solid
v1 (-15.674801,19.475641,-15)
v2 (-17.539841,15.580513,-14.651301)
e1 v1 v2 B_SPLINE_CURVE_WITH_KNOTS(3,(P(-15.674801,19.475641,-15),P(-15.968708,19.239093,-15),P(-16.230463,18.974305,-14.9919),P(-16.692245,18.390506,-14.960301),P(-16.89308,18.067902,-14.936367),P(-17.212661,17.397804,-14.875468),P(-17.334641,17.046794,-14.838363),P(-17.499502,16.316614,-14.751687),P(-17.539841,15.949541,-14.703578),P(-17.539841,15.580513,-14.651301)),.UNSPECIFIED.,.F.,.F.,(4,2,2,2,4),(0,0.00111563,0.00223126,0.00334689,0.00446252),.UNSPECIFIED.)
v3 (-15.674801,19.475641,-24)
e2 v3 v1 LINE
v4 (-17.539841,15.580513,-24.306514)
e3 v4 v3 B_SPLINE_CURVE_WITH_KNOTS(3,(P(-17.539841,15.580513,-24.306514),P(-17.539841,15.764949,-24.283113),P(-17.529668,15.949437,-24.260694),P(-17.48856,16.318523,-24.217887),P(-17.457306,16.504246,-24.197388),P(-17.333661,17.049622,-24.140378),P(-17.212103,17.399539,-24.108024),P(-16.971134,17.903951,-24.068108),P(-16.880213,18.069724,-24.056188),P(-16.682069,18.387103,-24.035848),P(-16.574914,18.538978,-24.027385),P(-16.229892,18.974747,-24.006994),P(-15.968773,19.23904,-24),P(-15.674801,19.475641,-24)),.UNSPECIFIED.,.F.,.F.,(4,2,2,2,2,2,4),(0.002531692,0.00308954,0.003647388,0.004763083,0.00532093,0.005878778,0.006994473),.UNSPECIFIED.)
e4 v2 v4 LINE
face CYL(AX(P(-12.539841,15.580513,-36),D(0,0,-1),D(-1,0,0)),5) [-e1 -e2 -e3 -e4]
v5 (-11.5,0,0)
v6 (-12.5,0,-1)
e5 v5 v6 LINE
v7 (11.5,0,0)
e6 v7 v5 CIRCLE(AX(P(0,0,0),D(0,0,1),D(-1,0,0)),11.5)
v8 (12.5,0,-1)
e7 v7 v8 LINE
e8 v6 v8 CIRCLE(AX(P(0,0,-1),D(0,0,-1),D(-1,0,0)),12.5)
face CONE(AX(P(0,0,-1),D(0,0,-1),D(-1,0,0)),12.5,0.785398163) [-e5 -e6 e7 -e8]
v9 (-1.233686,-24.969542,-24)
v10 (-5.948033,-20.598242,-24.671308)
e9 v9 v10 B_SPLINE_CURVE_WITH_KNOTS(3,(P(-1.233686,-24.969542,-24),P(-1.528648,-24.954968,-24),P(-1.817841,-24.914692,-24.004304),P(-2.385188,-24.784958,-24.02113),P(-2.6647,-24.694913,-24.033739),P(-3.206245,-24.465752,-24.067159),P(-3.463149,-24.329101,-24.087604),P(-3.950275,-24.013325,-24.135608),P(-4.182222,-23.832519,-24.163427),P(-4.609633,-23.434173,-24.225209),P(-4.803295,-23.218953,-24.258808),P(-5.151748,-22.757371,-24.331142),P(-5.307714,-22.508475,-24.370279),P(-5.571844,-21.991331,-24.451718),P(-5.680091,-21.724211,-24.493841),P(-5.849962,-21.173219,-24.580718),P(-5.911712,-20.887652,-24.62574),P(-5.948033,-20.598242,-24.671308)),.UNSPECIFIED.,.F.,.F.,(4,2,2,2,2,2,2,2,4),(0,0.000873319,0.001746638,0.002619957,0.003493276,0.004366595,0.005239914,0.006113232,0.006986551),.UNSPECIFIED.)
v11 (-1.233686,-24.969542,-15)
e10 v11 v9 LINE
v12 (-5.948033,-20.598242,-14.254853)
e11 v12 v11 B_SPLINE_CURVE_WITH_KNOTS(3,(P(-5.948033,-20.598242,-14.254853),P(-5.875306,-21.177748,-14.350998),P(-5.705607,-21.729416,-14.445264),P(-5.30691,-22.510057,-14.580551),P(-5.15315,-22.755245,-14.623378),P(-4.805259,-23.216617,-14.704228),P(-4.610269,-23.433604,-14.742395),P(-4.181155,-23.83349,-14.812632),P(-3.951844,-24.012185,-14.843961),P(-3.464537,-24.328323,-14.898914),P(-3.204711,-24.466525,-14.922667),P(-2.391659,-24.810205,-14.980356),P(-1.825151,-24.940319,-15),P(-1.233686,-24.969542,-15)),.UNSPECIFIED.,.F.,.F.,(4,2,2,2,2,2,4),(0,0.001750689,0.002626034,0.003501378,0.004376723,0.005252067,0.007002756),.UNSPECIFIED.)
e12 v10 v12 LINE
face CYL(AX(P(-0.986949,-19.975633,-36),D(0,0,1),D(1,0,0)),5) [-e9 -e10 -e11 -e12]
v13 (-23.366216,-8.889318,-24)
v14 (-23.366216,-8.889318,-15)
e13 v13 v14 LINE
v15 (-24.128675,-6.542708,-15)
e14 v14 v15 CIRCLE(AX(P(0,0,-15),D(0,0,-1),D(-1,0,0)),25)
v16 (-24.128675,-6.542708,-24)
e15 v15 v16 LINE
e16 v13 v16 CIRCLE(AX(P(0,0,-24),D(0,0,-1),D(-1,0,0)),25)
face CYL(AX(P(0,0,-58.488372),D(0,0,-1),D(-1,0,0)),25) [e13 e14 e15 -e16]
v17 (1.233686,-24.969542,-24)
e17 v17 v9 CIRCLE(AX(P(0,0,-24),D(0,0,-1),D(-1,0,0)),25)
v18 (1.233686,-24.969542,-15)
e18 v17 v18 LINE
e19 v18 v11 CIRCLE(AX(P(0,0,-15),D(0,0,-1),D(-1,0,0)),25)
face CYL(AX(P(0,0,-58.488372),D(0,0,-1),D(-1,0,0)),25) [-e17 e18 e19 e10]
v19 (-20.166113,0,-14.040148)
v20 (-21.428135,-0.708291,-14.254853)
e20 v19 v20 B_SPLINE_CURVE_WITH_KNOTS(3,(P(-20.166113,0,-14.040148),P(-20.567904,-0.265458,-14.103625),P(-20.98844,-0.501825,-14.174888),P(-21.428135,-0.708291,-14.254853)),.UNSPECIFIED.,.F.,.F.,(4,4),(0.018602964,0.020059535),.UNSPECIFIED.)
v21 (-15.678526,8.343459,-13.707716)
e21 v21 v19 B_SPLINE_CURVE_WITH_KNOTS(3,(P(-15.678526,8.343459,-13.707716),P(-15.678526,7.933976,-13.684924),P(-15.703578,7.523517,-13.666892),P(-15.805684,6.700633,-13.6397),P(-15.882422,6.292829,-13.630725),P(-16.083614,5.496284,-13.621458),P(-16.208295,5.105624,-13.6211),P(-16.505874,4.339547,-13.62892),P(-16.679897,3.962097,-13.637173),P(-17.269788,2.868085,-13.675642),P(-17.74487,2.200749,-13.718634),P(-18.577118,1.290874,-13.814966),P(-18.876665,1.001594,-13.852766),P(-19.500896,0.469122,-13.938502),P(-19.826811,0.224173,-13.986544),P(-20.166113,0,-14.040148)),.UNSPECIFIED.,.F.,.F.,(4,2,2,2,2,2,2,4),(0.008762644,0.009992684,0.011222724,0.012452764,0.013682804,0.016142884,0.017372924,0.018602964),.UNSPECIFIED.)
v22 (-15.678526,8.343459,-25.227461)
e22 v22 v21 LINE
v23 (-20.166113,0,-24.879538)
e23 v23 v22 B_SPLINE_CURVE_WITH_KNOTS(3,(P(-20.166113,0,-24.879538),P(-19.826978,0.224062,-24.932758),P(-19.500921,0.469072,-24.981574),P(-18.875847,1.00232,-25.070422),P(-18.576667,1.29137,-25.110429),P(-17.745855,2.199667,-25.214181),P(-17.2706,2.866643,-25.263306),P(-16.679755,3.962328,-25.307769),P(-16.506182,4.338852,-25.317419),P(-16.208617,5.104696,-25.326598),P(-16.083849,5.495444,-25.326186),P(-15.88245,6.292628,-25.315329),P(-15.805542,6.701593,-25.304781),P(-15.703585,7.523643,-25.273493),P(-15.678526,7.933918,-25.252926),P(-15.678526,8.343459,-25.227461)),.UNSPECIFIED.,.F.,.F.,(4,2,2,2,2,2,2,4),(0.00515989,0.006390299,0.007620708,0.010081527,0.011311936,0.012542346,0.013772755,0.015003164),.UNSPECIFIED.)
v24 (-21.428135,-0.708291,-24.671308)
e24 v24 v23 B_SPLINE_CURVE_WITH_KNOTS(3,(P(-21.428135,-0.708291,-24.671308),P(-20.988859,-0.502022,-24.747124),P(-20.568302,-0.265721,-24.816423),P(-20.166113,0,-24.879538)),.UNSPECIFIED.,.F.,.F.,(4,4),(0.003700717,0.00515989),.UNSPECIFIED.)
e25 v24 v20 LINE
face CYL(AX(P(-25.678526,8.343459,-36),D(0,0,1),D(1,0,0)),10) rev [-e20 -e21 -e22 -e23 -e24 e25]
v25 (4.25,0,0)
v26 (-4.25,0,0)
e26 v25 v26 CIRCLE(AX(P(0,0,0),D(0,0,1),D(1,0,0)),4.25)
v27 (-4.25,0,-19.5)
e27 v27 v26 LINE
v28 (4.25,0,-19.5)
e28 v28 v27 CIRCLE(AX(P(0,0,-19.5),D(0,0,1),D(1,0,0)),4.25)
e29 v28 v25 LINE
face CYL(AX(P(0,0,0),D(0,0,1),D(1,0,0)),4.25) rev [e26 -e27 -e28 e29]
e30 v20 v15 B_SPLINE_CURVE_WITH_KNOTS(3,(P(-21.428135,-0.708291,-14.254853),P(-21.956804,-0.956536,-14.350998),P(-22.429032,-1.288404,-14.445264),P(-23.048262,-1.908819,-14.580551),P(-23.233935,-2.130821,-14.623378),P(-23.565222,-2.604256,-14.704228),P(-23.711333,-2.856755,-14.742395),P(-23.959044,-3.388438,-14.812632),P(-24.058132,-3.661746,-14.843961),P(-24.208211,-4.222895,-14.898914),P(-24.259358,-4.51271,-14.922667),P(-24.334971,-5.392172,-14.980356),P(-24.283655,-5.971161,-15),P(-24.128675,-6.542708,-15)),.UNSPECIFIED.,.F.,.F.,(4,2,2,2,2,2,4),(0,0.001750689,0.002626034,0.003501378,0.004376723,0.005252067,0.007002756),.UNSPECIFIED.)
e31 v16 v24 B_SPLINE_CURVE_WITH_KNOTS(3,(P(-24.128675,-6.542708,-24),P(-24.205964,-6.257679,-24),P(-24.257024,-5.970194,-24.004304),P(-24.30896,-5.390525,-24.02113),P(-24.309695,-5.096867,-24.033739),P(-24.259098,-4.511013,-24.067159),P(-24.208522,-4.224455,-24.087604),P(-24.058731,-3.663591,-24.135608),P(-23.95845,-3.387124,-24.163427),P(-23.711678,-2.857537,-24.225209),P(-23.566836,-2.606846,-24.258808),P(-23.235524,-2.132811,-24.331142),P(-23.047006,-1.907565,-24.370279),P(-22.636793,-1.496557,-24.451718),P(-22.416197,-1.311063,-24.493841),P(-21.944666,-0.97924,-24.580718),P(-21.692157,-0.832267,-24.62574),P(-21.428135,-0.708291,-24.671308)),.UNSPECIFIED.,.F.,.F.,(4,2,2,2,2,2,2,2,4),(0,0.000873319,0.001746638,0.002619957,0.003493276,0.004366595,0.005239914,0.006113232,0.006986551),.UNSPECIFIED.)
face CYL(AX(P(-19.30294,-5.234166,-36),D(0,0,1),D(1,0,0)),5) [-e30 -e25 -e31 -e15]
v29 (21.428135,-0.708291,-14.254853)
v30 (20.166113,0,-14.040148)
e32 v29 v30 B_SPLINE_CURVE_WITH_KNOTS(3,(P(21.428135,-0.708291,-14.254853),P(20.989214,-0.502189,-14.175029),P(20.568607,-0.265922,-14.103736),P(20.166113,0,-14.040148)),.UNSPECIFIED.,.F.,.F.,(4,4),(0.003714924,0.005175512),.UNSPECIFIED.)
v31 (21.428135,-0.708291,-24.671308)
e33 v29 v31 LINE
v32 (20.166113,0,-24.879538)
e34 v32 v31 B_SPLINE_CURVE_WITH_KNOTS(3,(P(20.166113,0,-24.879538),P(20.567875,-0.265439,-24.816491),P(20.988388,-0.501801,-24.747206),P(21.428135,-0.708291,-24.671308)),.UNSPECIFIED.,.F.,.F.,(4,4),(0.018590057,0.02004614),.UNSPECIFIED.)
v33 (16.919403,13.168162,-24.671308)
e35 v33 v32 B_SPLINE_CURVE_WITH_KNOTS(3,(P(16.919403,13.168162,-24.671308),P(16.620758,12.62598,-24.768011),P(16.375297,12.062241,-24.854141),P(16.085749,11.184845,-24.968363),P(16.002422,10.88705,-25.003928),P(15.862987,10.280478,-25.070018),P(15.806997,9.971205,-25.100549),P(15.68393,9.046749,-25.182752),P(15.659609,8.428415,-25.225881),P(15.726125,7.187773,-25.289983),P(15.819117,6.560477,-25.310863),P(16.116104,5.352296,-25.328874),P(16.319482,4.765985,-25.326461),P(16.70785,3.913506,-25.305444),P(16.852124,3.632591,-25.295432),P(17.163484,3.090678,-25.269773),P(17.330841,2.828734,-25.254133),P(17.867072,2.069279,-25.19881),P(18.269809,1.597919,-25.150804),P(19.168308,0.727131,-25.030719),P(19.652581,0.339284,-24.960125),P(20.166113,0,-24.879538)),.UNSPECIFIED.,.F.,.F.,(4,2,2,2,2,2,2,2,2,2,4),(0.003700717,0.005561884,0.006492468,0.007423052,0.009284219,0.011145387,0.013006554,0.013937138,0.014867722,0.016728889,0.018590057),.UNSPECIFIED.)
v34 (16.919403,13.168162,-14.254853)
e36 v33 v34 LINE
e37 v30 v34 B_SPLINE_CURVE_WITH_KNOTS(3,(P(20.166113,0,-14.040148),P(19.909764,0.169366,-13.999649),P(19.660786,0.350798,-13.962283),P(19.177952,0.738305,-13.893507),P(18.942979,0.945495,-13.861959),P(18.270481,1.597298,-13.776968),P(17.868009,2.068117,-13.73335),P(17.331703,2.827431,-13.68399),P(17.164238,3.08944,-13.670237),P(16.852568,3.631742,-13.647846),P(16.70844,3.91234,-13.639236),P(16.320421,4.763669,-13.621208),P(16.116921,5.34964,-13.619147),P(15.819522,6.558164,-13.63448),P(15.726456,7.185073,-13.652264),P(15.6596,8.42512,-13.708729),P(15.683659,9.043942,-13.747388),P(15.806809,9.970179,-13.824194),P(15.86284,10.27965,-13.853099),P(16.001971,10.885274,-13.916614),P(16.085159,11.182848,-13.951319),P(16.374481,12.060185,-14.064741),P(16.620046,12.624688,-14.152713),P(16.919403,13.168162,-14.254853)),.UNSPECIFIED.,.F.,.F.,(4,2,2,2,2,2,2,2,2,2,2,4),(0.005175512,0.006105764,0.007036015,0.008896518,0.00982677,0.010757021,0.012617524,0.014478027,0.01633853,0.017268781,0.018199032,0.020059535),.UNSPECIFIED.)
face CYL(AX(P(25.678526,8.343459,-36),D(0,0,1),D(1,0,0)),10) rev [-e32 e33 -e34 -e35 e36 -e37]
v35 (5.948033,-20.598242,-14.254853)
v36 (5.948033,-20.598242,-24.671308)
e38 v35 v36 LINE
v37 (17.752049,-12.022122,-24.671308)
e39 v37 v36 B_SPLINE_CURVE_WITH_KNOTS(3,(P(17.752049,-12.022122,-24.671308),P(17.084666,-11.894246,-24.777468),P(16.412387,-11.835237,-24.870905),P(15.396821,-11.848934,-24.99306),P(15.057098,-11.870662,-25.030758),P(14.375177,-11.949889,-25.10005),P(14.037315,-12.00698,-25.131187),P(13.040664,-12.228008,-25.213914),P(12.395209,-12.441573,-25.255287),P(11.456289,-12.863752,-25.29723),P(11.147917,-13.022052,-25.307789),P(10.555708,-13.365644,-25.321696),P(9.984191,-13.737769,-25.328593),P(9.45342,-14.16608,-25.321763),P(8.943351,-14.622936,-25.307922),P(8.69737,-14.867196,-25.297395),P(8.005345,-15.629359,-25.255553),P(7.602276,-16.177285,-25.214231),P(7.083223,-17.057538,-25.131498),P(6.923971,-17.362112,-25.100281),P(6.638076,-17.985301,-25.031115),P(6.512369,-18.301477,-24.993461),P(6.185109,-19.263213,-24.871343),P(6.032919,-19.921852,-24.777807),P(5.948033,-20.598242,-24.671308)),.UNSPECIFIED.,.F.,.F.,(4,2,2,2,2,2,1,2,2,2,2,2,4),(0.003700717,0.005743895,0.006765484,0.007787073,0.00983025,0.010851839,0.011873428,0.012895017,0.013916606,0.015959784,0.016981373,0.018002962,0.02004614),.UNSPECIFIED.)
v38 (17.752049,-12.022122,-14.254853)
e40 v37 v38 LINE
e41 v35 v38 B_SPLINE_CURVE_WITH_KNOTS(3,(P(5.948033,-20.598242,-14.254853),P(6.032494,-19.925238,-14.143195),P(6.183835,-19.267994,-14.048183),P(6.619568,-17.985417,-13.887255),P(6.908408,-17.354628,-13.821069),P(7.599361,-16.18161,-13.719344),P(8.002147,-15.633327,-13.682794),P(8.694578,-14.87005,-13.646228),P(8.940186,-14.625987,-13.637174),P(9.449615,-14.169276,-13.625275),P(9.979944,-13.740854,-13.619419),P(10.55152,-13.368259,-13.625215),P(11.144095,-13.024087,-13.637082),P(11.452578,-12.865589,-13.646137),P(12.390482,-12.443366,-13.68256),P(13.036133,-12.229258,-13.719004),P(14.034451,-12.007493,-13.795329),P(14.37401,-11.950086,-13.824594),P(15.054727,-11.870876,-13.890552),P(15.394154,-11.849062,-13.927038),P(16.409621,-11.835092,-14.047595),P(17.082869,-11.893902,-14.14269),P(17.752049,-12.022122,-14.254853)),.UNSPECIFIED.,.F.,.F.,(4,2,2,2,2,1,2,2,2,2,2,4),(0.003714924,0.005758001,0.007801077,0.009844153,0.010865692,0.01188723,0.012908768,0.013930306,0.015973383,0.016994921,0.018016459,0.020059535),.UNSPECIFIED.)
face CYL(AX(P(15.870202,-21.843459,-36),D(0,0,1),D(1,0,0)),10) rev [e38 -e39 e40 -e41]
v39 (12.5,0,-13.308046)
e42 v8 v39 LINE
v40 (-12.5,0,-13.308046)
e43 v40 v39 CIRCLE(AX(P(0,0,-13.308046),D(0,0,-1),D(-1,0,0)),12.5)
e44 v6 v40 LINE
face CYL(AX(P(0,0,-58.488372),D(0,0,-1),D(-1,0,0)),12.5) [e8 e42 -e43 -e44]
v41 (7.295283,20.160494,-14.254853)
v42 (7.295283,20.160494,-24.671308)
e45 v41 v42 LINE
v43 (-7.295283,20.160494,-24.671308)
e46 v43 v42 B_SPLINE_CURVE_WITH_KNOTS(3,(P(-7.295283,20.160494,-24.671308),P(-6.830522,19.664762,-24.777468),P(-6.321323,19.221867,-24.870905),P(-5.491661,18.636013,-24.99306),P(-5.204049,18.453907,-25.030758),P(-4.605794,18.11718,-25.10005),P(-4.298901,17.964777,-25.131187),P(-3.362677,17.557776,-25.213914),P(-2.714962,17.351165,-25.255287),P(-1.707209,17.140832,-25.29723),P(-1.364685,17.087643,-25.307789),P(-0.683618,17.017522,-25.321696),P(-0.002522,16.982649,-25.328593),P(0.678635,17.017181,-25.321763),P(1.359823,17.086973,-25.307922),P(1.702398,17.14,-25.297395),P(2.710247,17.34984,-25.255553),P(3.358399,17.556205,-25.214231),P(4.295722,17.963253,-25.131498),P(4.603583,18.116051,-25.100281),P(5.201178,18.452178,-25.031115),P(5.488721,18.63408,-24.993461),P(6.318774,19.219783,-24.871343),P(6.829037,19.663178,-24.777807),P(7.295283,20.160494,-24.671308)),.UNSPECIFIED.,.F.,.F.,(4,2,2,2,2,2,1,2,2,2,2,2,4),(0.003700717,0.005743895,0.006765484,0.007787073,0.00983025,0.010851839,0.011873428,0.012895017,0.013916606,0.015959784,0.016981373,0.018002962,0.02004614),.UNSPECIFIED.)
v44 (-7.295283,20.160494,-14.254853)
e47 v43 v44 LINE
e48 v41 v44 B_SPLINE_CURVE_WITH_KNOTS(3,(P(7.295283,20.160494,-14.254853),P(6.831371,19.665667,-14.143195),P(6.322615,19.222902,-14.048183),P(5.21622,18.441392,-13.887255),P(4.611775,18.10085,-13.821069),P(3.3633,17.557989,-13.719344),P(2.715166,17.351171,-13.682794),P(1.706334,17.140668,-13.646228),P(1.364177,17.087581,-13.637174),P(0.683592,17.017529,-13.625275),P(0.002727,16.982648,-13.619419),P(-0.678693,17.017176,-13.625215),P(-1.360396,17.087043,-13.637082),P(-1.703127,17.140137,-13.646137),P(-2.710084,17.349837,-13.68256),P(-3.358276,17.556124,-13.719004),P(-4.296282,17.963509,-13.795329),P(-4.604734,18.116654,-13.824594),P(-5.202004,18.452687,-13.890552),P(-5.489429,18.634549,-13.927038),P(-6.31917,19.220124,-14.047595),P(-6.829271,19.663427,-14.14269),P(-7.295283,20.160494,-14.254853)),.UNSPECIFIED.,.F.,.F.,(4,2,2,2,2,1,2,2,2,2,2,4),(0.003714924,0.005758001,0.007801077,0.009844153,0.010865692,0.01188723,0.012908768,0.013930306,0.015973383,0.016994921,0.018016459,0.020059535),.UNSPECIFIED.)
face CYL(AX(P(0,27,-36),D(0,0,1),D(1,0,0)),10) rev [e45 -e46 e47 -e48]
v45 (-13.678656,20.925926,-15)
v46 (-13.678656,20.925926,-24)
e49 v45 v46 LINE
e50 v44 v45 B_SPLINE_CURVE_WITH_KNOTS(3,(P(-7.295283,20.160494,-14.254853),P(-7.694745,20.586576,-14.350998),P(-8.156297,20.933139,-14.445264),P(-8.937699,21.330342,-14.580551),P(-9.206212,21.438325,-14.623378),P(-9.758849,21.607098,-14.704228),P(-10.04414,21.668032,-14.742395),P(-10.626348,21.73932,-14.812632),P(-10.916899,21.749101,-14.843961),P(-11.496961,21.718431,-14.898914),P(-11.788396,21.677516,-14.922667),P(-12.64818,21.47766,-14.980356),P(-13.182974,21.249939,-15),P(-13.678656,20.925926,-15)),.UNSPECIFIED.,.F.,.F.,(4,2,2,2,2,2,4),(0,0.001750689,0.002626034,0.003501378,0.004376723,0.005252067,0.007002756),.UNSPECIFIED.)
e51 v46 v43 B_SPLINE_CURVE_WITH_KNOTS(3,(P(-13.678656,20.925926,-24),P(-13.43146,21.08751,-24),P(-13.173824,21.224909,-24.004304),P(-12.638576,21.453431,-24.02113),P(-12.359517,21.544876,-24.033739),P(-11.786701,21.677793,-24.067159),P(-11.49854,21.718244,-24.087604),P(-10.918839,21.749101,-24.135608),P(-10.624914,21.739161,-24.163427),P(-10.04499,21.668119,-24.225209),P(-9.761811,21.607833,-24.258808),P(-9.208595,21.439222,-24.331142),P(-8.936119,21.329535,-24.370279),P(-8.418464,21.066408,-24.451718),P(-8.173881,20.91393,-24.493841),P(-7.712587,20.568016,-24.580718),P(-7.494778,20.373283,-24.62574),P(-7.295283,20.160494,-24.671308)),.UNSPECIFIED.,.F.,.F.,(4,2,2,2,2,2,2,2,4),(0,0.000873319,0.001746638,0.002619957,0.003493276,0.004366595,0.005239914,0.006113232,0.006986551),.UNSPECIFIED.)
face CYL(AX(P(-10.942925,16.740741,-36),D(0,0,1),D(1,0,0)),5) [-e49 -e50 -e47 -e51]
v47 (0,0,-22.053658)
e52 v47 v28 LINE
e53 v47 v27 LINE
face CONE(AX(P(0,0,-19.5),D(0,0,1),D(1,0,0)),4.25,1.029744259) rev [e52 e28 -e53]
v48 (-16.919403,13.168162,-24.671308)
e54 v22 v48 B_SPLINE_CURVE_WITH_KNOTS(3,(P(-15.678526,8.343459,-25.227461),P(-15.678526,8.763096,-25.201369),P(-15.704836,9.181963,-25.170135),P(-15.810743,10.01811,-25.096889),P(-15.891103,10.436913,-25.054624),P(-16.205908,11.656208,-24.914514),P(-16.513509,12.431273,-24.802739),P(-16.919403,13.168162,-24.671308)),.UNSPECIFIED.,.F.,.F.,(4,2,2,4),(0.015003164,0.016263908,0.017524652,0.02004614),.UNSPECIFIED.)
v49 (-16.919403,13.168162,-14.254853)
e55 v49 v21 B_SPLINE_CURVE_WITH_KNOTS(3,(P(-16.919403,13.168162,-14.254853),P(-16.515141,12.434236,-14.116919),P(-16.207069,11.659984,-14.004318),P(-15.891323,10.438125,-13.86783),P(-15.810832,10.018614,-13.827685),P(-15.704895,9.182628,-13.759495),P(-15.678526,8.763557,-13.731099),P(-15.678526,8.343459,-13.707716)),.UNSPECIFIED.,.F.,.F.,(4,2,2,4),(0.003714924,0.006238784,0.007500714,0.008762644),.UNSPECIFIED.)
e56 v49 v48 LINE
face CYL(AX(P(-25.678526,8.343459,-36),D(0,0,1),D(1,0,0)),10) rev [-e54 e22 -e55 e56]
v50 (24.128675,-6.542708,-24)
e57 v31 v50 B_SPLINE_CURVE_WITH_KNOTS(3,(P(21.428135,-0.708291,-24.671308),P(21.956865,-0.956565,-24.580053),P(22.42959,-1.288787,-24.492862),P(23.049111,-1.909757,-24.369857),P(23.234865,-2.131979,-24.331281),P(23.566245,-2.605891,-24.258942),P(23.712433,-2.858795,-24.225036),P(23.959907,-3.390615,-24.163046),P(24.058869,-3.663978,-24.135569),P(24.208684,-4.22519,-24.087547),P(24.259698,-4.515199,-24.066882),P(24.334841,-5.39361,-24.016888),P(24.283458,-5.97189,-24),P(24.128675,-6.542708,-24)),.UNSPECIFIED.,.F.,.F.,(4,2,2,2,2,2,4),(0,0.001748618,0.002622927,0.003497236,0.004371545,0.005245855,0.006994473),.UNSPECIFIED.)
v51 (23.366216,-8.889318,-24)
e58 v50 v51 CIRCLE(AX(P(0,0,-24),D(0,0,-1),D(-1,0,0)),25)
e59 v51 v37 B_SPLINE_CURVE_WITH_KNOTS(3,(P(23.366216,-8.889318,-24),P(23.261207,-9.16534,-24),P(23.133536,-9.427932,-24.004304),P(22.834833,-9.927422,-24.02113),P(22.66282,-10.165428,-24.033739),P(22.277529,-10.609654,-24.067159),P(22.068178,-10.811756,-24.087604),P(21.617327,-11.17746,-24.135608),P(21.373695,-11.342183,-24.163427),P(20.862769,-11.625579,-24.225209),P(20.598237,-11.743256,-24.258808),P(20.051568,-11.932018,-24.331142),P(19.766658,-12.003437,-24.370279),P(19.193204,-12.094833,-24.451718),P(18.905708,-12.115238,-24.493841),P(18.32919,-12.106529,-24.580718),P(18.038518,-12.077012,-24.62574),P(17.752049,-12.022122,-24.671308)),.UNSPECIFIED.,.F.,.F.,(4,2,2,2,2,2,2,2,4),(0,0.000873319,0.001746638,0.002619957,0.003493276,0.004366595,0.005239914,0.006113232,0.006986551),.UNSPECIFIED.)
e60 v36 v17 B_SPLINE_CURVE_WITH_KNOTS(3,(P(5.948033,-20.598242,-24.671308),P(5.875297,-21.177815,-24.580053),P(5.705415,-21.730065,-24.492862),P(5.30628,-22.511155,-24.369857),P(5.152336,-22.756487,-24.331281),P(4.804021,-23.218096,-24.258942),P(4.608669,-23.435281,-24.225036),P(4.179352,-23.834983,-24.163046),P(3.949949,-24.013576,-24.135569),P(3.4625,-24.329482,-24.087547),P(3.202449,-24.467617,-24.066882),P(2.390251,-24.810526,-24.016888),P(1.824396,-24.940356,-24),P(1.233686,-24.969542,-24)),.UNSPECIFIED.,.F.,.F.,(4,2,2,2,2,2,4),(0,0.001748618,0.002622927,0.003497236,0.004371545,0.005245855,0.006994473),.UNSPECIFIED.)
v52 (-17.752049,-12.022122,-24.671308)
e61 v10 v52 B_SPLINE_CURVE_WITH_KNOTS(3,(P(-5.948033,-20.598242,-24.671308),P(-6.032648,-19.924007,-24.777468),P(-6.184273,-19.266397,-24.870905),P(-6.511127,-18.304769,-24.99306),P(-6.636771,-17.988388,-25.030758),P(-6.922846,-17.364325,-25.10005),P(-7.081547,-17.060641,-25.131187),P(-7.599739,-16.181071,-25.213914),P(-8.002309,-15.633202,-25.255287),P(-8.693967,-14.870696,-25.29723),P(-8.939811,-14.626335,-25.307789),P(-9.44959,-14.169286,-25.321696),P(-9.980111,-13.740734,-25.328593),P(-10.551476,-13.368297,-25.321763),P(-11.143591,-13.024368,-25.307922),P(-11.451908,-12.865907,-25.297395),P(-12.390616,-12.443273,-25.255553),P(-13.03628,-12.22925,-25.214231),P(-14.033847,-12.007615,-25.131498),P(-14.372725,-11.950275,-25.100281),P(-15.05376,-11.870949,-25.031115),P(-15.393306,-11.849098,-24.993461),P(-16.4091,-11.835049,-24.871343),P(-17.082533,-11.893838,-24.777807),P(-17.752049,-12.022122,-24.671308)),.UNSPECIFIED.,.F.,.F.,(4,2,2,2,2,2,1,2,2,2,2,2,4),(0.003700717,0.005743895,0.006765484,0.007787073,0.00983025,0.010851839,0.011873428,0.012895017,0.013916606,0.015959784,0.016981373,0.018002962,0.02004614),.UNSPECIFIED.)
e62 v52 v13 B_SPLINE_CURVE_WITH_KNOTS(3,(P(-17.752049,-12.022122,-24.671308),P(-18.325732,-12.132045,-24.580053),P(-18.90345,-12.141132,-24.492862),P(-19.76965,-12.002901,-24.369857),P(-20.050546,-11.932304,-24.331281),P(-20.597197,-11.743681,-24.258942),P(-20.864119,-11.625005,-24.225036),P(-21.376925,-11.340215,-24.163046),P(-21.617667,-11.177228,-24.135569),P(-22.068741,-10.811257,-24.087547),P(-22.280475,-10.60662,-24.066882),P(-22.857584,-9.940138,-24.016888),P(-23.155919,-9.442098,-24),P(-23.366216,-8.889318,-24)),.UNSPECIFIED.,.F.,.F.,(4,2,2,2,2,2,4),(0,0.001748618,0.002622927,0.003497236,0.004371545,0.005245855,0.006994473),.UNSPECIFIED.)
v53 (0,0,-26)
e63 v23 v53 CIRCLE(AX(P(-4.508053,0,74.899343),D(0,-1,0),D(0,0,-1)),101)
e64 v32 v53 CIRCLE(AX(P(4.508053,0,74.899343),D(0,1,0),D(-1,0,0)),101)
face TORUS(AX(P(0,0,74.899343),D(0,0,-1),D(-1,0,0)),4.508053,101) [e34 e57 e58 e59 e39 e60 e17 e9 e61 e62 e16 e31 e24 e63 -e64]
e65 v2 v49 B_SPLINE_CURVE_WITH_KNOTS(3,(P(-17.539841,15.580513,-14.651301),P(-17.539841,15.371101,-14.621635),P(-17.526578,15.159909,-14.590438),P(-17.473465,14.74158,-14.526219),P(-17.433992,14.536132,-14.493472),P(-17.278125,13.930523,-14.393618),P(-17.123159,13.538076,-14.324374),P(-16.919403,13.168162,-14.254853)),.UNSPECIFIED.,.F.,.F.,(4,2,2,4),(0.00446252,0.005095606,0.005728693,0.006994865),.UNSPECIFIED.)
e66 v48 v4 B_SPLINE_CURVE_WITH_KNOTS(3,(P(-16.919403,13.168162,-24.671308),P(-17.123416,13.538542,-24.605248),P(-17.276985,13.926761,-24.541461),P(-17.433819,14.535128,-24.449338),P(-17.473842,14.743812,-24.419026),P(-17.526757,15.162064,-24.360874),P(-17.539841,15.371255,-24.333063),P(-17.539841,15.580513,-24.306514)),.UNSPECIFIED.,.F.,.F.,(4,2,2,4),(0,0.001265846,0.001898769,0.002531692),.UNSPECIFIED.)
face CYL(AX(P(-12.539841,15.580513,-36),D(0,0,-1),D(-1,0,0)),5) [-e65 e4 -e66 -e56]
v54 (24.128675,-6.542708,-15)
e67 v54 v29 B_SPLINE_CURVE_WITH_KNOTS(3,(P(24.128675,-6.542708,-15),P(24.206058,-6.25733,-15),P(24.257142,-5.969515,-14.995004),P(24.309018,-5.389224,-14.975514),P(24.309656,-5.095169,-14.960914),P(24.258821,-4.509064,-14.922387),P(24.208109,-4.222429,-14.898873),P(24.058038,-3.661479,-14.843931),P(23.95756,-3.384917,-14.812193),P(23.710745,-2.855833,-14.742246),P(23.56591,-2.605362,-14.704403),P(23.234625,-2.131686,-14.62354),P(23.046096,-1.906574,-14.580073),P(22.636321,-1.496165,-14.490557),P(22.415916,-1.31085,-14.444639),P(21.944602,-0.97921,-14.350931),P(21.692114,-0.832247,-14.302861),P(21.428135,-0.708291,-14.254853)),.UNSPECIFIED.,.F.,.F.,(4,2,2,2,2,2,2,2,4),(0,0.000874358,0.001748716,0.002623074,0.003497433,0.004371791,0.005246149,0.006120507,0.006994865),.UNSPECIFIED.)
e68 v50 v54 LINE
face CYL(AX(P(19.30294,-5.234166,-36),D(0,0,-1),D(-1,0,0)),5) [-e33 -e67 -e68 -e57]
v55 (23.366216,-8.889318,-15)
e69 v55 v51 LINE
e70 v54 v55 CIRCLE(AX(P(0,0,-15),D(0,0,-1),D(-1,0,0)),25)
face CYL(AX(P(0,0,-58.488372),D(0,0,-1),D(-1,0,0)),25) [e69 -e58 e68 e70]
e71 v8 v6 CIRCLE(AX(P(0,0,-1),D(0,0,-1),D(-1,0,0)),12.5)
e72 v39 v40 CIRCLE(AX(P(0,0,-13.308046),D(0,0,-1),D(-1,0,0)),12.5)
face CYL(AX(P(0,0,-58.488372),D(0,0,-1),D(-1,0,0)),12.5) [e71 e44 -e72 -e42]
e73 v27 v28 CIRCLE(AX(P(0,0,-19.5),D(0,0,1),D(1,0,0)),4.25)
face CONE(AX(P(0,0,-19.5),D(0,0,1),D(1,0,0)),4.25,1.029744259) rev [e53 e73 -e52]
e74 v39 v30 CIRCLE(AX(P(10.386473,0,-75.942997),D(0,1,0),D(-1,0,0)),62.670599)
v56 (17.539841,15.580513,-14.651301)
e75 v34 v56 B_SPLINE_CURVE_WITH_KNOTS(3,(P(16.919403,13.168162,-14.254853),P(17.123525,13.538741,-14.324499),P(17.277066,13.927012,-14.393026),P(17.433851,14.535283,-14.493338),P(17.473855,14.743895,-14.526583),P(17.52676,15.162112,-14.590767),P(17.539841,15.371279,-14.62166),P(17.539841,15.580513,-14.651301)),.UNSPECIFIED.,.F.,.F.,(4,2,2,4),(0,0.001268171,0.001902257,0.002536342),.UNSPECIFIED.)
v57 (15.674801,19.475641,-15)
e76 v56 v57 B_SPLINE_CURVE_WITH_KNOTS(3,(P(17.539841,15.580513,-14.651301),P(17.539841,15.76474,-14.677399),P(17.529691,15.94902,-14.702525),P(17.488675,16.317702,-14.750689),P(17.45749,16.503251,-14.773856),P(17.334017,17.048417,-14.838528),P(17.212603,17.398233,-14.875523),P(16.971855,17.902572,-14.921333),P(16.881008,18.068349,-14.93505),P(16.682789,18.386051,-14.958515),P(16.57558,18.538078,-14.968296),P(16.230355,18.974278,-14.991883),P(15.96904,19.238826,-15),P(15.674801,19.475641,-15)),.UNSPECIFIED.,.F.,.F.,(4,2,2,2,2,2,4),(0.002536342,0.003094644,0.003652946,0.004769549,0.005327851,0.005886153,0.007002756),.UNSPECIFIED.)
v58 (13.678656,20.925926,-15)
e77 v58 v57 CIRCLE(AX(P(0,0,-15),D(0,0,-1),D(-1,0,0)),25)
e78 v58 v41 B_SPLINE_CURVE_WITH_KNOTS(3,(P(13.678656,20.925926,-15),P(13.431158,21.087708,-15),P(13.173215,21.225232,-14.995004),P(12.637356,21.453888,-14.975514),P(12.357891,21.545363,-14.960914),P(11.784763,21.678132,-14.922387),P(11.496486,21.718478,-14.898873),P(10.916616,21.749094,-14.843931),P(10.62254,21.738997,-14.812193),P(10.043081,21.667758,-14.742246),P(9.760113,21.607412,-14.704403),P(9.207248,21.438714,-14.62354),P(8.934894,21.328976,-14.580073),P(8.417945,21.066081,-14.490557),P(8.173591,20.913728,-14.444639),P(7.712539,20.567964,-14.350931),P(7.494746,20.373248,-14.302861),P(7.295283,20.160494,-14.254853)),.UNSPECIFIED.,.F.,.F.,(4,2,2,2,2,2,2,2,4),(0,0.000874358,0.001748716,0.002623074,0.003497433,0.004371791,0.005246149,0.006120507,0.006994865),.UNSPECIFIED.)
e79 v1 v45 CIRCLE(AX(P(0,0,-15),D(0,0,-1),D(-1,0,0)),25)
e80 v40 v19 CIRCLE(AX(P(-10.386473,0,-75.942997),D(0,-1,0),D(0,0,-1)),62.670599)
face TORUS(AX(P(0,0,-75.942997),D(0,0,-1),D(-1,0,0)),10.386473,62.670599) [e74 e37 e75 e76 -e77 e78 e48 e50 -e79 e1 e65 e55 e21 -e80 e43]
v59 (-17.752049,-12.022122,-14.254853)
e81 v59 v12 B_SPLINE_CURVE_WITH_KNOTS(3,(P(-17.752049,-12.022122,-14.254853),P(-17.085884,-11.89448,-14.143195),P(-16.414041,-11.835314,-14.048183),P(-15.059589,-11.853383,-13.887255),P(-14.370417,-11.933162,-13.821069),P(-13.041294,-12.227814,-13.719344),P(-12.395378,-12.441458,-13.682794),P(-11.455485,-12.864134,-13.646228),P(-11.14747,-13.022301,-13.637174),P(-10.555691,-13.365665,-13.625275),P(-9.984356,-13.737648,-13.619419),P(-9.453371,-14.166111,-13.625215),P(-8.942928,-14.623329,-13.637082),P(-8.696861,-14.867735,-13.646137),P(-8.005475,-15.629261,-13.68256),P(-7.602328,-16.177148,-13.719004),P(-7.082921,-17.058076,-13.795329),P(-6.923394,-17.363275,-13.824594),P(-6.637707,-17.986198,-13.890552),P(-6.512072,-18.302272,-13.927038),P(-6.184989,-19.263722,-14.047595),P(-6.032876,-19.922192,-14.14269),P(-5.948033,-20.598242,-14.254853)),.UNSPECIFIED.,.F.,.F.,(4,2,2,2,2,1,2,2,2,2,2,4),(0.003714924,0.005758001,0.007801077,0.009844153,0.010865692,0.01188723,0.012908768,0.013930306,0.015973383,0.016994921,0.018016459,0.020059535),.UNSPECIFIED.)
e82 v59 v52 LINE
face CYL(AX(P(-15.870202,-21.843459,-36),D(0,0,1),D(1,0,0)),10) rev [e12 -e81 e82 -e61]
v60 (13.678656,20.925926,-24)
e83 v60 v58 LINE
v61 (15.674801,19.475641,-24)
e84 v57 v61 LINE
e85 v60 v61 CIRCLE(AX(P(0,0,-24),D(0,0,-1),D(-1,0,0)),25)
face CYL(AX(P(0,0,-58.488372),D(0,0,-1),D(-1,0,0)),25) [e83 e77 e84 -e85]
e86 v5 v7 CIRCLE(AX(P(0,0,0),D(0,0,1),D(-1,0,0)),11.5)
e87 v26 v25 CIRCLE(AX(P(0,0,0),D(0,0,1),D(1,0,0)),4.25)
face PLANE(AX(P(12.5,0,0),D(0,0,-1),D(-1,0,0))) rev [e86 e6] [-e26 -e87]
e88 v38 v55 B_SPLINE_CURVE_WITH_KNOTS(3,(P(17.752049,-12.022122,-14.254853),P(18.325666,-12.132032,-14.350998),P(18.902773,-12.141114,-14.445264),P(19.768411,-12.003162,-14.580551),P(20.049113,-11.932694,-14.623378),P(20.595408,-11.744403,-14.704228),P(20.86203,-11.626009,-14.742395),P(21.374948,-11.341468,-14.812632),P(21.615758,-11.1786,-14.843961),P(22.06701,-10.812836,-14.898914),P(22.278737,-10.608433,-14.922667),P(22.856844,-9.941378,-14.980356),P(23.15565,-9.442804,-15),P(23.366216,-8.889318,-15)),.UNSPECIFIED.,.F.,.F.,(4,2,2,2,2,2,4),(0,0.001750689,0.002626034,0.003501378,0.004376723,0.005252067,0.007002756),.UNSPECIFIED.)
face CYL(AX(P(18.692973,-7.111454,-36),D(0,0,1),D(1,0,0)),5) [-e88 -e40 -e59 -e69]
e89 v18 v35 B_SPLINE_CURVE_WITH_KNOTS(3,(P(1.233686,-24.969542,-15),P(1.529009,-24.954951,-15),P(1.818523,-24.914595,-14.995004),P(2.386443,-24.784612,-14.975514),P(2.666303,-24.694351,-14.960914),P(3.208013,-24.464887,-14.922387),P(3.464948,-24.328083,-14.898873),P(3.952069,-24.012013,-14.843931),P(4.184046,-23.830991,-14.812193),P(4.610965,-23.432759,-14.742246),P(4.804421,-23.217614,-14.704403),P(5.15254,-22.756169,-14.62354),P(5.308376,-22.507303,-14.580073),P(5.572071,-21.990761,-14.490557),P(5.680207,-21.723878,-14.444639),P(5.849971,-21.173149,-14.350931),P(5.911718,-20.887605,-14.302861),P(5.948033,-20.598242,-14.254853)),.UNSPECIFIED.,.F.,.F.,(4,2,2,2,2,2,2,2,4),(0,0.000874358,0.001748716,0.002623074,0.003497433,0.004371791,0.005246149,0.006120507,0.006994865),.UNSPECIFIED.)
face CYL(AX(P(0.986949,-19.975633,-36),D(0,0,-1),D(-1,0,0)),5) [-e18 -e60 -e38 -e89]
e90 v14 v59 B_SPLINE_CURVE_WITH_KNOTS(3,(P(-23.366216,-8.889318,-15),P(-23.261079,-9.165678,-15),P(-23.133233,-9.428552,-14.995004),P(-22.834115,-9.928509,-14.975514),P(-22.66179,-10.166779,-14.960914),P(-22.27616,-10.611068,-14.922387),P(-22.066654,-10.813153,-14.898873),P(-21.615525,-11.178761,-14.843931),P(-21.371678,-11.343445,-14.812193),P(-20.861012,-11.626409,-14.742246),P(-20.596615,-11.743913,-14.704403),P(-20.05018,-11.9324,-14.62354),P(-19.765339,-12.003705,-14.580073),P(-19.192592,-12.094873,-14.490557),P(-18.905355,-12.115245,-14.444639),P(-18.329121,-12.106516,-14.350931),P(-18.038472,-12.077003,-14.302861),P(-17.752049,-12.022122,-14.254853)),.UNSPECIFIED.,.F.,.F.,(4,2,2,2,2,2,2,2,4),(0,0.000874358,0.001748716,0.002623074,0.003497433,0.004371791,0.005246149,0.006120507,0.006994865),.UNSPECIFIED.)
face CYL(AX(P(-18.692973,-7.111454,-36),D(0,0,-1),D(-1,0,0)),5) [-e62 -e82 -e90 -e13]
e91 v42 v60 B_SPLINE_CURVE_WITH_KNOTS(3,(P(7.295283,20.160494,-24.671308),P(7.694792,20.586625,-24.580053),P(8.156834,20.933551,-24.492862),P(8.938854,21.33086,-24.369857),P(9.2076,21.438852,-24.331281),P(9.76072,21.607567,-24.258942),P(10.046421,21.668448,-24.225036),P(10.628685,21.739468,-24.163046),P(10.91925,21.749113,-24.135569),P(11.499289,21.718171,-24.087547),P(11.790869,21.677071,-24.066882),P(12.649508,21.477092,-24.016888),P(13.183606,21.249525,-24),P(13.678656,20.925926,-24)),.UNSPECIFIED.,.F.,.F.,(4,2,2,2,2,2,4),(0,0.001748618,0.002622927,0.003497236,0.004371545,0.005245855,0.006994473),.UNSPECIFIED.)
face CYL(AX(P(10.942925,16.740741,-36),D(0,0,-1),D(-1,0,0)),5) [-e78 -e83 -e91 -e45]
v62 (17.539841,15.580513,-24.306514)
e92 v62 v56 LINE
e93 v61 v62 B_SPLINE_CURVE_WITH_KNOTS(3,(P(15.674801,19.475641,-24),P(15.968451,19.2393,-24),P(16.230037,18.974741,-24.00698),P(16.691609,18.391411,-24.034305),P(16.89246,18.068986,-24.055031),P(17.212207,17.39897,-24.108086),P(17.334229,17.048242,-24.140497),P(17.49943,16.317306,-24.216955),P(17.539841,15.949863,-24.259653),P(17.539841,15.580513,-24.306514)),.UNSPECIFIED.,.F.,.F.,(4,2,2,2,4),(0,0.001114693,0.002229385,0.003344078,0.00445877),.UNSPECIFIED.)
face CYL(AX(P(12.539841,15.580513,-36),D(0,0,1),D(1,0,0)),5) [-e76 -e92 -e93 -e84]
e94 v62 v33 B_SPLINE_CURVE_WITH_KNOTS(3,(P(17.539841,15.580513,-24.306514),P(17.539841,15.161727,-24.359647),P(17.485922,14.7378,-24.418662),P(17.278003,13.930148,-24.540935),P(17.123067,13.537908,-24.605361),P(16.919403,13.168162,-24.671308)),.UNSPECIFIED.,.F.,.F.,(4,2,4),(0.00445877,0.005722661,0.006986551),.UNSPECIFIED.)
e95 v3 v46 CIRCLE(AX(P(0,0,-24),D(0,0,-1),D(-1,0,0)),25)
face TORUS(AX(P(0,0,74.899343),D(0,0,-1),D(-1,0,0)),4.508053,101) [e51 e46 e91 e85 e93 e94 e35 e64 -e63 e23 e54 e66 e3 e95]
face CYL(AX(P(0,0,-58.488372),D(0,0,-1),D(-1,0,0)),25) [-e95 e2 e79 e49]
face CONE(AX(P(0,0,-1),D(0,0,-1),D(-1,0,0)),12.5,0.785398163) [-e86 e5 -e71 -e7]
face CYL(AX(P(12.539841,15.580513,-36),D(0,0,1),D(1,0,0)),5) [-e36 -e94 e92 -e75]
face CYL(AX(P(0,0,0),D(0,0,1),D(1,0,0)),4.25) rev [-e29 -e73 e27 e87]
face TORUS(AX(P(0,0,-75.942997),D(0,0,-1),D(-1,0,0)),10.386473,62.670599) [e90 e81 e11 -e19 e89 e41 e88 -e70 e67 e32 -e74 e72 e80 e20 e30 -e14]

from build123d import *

# Parameters (mm, degrees)
HOLE_WIZARD_M10_1_D      = 8.5
HOLE_WIZARD_M10_1_DEPTH  = 19.5
HOLE_WIZARD_M10_1_TIP    = 2.553657631
SKETCH_4_R               = 10
CUT_EXTRUDE_2_DEPTH      = 36
PATTERN_CIRCULAR_1_COUNT = 5
FILLET_2_R               = 5
CHAMFER_1_SIZE           = 1


with BuildPart() as part:
    # 草图1 → 旋转1 (revolve)
    with BuildSketch(Plane(origin=(0, 0, 0), x_dir=(1, 0, 0), z_dir=(0, 1, 0)), mode=Mode.PRIVATE) as revolve_1_sk:
        with BuildLine():
            Line((25, 24), (25, 15))
            ThreePointArc((25, 15), (18.792676706, 13.838731535), (12.5, 13.30804631))
            Line((12.5, 13.30804631), (12.5, 0))
            Line((12.5, 0), (0, 0))
            Line((0, 0), (0, 26))
            ThreePointArc((0, 26), (12.562319993, 25.778999912), (25, 24))
        make_face()
    revolve(revolve_1_sk.sketch.rotate(Axis((0, 0, -58.488372093), (0, 0, 1)), 180), axis=Axis((0, 0, -58.488372093), (0, 0, 1)))

    # M10 螺纹孔1
    with Locations(Plane.XY):
        with Locations((0, 0)):
            Hole(HOLE_WIZARD_M10_1_D / 2, depth=HOLE_WIZARD_M10_1_DEPTH)
            with Locations((0, 0, -(HOLE_WIZARD_M10_1_DEPTH + HOLE_WIZARD_M10_1_TIP / 2))):  # 118° drill point
                Cone(0, HOLE_WIZARD_M10_1_D / 2, HOLE_WIZARD_M10_1_TIP, mode=Mode.SUBTRACT)

    # 草图4 → 切除-拉伸2 (cut)
    with BuildSketch(Plane.XY):
        with Locations((0, 27)):
            Circle(SKETCH_4_R)
    cut_extrude_2 = extrude(amount=-CUT_EXTRUDE_2_DEPTH, mode=Mode.SUBTRACT)

    # 阵列(圆周)1: 切除-拉伸2 ×5 about axis
    pattern_circular_1_axis = Axis((0, 0, 0), (0, 0, 1))
    for i in range(1, PATTERN_CIRCULAR_1_COUNT):
        add(cut_extrude_2.rotate(pattern_circular_1_axis, i * 360 / PATTERN_CIRCULAR_1_COUNT), mode=Mode.SUBTRACT)

    # 圆角2
    fillet_2_edges = [part.edges().sort_by_distance(p)[0] for p in [
        (-24.946822672, -1.629735742, -19.5),
        (-19.224468863, 15.981858369, -19.5),
        (-9.258962958, 23.222222222, -19.5),
        (9.258962958, 23.222222222, -19.5),
        (-6.159021364, -24.229454303, -19.5),
        (-21.140338131, -13.344890547, -19.5),
        (21.140338131, -13.344890547, -19.5),
        (6.159021364, -24.229454303, -19.5),
        (19.224468863, 15.981858369, -19.5),
        (24.946822672, -1.629735742, -19.5),
    ]]
    fillet(fillet_2_edges, radius=FILLET_2_R)

    # 倒角1
    chamfer_1_edges = [part.edges().sort_by_distance(p)[0] for p in [
        (12.5, 0, 0),
    ]]
    chamfer(chamfer_1_edges, length=CHAMFER_1_SIZE)


solid = part.part
